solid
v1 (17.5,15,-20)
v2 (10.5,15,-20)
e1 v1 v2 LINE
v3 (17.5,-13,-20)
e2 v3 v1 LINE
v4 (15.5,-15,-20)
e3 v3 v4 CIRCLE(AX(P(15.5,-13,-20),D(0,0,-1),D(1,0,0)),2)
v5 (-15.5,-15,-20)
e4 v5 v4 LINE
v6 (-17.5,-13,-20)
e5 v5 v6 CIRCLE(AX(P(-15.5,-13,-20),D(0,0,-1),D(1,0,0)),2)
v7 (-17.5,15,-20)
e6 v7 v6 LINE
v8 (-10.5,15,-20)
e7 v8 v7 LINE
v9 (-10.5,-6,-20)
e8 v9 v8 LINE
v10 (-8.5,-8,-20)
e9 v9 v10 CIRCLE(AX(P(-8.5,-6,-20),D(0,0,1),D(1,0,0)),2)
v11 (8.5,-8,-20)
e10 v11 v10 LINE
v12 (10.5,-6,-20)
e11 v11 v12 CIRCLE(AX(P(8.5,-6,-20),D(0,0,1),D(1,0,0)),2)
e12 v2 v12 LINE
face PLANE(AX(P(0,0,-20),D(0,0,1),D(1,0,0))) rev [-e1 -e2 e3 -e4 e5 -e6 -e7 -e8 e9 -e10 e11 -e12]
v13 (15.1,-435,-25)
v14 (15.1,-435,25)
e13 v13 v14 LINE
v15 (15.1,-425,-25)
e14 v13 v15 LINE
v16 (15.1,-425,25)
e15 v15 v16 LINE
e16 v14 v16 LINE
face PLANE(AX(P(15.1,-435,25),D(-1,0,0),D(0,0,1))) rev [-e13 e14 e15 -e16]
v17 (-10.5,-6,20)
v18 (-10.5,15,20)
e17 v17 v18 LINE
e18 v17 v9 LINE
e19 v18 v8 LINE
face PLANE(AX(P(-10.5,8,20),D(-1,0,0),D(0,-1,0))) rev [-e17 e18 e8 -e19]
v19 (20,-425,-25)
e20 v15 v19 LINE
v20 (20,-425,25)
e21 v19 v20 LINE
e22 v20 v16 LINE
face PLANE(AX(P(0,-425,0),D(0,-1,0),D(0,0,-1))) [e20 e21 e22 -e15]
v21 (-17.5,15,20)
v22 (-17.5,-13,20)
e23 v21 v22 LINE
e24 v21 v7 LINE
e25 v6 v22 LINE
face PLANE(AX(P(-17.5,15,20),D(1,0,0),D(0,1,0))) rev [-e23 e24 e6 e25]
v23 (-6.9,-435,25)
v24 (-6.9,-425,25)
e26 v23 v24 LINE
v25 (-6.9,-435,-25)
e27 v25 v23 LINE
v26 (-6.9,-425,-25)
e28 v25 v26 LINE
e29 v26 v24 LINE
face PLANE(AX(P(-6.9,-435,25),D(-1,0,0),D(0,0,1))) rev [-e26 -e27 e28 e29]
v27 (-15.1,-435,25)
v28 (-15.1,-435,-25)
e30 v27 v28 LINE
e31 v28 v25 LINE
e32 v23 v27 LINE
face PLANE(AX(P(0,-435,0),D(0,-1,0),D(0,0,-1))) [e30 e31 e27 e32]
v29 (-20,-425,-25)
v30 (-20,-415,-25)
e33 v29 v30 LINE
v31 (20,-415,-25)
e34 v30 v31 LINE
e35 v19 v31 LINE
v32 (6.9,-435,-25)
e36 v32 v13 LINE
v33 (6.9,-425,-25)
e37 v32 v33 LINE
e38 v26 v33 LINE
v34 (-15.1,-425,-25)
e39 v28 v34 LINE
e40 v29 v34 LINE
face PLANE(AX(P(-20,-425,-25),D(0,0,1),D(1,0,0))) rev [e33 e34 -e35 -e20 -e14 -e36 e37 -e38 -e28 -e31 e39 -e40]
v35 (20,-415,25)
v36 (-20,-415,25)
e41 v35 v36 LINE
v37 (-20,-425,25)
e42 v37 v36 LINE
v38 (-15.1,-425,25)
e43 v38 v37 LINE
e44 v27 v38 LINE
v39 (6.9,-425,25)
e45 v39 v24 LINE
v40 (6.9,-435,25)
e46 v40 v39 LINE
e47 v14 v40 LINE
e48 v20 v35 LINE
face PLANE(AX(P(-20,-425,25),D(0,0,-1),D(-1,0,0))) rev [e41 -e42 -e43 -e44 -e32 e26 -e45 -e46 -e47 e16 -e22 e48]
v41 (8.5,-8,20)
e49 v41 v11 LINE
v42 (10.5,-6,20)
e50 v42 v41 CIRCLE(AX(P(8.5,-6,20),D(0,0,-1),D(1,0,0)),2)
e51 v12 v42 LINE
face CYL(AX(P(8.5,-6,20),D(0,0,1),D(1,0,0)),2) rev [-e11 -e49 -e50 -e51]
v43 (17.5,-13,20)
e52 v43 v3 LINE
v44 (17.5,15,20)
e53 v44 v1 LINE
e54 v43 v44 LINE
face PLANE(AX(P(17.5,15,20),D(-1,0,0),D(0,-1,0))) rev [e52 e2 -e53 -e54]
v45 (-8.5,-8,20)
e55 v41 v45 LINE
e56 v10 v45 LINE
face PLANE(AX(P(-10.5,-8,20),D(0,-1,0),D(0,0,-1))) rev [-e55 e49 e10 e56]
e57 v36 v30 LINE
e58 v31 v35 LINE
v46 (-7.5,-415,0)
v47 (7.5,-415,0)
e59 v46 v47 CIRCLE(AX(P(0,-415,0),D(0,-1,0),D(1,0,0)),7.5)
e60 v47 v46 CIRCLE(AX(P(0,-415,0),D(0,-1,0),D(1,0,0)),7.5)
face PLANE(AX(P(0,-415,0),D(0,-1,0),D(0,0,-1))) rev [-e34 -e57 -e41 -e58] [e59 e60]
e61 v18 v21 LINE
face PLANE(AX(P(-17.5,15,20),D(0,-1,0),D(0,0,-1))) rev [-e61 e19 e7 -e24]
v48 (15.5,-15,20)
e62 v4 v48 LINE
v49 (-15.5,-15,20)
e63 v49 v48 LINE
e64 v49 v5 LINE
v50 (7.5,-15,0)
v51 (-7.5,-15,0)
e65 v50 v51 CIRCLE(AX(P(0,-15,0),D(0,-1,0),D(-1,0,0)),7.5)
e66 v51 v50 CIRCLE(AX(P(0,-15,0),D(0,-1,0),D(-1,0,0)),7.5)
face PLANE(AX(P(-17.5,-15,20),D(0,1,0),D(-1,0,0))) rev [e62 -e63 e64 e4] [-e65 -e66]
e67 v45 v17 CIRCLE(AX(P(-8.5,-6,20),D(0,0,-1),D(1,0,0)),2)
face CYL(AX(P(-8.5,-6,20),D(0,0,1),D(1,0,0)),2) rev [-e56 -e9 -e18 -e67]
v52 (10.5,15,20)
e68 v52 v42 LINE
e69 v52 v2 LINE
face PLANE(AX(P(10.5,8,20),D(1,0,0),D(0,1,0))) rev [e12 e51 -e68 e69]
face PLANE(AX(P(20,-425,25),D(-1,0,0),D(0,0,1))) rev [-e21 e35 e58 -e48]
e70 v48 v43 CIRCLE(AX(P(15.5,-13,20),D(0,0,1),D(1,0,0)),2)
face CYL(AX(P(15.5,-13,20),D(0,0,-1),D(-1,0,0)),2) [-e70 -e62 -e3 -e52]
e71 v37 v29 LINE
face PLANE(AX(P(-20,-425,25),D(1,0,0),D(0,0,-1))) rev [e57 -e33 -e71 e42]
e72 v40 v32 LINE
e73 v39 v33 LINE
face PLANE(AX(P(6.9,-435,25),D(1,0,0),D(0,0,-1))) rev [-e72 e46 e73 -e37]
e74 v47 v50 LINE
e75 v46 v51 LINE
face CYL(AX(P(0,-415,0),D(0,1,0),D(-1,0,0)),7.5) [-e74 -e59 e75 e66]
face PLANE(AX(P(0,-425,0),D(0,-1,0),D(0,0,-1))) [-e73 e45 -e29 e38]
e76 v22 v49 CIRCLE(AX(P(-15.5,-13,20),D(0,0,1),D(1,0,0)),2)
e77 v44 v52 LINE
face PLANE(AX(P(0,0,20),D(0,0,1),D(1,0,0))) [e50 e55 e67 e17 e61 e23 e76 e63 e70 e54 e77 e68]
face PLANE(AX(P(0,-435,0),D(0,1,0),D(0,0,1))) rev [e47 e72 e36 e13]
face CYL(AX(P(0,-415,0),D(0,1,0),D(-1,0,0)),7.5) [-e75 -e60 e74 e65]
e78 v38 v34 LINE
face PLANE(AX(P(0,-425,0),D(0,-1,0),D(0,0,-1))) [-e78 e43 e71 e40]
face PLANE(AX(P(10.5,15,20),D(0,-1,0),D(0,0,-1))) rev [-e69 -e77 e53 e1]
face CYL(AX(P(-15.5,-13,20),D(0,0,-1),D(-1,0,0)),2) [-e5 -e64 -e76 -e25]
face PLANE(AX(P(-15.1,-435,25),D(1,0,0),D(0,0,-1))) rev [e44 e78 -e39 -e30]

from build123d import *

# Parameters (mm, degrees)
BOSS_EXTRUDE1_DEPTH = 20
FILLET1_R           = 2
SKETCH2_R           = 7.5
BOSS_EXTRUDE2_DEPTH = 400
SKETCH3_W           = 40
SKETCH3_H           = 50
BOSS_EXTRUDE3_DEPTH = 10
SKETCH4_W           = 8.2
SKETCH4_H           = 50
BOSS_EXTRUDE4_DEPTH = 10


with BuildPart() as part:
    # Sketch1 → Boss-Extrude1 (new, symmetric)
    with BuildSketch(Plane.XY):
        Polygon((-10.5, 8), (-10.5, -8), (10.5, -8), (10.5, 8), (10.5, 15), (17.5, 15), (17.5, -15), (-17.5, -15), (-17.5, 15), (-10.5, 15), align=None)
    extrude(amount=BOSS_EXTRUDE1_DEPTH, both=True)

    # Fillet1
    fillet1_edges = [part.edges().sort_by_distance(p)[0] for p in [
        (17.5, -15, 0),
        (-17.5, -15, 0),
        (-10.5, -8, 0),
        (10.5, -8, 0),
    ]]
    fillet(fillet1_edges, radius=FILLET1_R)

    # Sketch2 → Boss-Extrude2 (add)
    with BuildSketch(Plane.XZ.offset(15)):
        with Locations(Location((0, 0, 0), (0, 0, 180))):
            Circle(SKETCH2_R)
    extrude(amount=BOSS_EXTRUDE2_DEPTH)

    # Sketch3 → Boss-Extrude3 (add)
    with BuildSketch(Plane.XZ.offset(415)):
        Rectangle(SKETCH3_W, SKETCH3_H)
    extrude(amount=BOSS_EXTRUDE3_DEPTH)

    # Sketch4 → Boss-Extrude4 (add)
    with BuildSketch(Plane.XZ.offset(425)):
        with Locations((-11, 0)):
            Rectangle(SKETCH4_W, SKETCH4_H)
        with Locations((11, 0)):
            Rectangle(SKETCH4_W, SKETCH4_H)
    extrude(amount=BOSS_EXTRUDE4_DEPTH)


solid = part.part
